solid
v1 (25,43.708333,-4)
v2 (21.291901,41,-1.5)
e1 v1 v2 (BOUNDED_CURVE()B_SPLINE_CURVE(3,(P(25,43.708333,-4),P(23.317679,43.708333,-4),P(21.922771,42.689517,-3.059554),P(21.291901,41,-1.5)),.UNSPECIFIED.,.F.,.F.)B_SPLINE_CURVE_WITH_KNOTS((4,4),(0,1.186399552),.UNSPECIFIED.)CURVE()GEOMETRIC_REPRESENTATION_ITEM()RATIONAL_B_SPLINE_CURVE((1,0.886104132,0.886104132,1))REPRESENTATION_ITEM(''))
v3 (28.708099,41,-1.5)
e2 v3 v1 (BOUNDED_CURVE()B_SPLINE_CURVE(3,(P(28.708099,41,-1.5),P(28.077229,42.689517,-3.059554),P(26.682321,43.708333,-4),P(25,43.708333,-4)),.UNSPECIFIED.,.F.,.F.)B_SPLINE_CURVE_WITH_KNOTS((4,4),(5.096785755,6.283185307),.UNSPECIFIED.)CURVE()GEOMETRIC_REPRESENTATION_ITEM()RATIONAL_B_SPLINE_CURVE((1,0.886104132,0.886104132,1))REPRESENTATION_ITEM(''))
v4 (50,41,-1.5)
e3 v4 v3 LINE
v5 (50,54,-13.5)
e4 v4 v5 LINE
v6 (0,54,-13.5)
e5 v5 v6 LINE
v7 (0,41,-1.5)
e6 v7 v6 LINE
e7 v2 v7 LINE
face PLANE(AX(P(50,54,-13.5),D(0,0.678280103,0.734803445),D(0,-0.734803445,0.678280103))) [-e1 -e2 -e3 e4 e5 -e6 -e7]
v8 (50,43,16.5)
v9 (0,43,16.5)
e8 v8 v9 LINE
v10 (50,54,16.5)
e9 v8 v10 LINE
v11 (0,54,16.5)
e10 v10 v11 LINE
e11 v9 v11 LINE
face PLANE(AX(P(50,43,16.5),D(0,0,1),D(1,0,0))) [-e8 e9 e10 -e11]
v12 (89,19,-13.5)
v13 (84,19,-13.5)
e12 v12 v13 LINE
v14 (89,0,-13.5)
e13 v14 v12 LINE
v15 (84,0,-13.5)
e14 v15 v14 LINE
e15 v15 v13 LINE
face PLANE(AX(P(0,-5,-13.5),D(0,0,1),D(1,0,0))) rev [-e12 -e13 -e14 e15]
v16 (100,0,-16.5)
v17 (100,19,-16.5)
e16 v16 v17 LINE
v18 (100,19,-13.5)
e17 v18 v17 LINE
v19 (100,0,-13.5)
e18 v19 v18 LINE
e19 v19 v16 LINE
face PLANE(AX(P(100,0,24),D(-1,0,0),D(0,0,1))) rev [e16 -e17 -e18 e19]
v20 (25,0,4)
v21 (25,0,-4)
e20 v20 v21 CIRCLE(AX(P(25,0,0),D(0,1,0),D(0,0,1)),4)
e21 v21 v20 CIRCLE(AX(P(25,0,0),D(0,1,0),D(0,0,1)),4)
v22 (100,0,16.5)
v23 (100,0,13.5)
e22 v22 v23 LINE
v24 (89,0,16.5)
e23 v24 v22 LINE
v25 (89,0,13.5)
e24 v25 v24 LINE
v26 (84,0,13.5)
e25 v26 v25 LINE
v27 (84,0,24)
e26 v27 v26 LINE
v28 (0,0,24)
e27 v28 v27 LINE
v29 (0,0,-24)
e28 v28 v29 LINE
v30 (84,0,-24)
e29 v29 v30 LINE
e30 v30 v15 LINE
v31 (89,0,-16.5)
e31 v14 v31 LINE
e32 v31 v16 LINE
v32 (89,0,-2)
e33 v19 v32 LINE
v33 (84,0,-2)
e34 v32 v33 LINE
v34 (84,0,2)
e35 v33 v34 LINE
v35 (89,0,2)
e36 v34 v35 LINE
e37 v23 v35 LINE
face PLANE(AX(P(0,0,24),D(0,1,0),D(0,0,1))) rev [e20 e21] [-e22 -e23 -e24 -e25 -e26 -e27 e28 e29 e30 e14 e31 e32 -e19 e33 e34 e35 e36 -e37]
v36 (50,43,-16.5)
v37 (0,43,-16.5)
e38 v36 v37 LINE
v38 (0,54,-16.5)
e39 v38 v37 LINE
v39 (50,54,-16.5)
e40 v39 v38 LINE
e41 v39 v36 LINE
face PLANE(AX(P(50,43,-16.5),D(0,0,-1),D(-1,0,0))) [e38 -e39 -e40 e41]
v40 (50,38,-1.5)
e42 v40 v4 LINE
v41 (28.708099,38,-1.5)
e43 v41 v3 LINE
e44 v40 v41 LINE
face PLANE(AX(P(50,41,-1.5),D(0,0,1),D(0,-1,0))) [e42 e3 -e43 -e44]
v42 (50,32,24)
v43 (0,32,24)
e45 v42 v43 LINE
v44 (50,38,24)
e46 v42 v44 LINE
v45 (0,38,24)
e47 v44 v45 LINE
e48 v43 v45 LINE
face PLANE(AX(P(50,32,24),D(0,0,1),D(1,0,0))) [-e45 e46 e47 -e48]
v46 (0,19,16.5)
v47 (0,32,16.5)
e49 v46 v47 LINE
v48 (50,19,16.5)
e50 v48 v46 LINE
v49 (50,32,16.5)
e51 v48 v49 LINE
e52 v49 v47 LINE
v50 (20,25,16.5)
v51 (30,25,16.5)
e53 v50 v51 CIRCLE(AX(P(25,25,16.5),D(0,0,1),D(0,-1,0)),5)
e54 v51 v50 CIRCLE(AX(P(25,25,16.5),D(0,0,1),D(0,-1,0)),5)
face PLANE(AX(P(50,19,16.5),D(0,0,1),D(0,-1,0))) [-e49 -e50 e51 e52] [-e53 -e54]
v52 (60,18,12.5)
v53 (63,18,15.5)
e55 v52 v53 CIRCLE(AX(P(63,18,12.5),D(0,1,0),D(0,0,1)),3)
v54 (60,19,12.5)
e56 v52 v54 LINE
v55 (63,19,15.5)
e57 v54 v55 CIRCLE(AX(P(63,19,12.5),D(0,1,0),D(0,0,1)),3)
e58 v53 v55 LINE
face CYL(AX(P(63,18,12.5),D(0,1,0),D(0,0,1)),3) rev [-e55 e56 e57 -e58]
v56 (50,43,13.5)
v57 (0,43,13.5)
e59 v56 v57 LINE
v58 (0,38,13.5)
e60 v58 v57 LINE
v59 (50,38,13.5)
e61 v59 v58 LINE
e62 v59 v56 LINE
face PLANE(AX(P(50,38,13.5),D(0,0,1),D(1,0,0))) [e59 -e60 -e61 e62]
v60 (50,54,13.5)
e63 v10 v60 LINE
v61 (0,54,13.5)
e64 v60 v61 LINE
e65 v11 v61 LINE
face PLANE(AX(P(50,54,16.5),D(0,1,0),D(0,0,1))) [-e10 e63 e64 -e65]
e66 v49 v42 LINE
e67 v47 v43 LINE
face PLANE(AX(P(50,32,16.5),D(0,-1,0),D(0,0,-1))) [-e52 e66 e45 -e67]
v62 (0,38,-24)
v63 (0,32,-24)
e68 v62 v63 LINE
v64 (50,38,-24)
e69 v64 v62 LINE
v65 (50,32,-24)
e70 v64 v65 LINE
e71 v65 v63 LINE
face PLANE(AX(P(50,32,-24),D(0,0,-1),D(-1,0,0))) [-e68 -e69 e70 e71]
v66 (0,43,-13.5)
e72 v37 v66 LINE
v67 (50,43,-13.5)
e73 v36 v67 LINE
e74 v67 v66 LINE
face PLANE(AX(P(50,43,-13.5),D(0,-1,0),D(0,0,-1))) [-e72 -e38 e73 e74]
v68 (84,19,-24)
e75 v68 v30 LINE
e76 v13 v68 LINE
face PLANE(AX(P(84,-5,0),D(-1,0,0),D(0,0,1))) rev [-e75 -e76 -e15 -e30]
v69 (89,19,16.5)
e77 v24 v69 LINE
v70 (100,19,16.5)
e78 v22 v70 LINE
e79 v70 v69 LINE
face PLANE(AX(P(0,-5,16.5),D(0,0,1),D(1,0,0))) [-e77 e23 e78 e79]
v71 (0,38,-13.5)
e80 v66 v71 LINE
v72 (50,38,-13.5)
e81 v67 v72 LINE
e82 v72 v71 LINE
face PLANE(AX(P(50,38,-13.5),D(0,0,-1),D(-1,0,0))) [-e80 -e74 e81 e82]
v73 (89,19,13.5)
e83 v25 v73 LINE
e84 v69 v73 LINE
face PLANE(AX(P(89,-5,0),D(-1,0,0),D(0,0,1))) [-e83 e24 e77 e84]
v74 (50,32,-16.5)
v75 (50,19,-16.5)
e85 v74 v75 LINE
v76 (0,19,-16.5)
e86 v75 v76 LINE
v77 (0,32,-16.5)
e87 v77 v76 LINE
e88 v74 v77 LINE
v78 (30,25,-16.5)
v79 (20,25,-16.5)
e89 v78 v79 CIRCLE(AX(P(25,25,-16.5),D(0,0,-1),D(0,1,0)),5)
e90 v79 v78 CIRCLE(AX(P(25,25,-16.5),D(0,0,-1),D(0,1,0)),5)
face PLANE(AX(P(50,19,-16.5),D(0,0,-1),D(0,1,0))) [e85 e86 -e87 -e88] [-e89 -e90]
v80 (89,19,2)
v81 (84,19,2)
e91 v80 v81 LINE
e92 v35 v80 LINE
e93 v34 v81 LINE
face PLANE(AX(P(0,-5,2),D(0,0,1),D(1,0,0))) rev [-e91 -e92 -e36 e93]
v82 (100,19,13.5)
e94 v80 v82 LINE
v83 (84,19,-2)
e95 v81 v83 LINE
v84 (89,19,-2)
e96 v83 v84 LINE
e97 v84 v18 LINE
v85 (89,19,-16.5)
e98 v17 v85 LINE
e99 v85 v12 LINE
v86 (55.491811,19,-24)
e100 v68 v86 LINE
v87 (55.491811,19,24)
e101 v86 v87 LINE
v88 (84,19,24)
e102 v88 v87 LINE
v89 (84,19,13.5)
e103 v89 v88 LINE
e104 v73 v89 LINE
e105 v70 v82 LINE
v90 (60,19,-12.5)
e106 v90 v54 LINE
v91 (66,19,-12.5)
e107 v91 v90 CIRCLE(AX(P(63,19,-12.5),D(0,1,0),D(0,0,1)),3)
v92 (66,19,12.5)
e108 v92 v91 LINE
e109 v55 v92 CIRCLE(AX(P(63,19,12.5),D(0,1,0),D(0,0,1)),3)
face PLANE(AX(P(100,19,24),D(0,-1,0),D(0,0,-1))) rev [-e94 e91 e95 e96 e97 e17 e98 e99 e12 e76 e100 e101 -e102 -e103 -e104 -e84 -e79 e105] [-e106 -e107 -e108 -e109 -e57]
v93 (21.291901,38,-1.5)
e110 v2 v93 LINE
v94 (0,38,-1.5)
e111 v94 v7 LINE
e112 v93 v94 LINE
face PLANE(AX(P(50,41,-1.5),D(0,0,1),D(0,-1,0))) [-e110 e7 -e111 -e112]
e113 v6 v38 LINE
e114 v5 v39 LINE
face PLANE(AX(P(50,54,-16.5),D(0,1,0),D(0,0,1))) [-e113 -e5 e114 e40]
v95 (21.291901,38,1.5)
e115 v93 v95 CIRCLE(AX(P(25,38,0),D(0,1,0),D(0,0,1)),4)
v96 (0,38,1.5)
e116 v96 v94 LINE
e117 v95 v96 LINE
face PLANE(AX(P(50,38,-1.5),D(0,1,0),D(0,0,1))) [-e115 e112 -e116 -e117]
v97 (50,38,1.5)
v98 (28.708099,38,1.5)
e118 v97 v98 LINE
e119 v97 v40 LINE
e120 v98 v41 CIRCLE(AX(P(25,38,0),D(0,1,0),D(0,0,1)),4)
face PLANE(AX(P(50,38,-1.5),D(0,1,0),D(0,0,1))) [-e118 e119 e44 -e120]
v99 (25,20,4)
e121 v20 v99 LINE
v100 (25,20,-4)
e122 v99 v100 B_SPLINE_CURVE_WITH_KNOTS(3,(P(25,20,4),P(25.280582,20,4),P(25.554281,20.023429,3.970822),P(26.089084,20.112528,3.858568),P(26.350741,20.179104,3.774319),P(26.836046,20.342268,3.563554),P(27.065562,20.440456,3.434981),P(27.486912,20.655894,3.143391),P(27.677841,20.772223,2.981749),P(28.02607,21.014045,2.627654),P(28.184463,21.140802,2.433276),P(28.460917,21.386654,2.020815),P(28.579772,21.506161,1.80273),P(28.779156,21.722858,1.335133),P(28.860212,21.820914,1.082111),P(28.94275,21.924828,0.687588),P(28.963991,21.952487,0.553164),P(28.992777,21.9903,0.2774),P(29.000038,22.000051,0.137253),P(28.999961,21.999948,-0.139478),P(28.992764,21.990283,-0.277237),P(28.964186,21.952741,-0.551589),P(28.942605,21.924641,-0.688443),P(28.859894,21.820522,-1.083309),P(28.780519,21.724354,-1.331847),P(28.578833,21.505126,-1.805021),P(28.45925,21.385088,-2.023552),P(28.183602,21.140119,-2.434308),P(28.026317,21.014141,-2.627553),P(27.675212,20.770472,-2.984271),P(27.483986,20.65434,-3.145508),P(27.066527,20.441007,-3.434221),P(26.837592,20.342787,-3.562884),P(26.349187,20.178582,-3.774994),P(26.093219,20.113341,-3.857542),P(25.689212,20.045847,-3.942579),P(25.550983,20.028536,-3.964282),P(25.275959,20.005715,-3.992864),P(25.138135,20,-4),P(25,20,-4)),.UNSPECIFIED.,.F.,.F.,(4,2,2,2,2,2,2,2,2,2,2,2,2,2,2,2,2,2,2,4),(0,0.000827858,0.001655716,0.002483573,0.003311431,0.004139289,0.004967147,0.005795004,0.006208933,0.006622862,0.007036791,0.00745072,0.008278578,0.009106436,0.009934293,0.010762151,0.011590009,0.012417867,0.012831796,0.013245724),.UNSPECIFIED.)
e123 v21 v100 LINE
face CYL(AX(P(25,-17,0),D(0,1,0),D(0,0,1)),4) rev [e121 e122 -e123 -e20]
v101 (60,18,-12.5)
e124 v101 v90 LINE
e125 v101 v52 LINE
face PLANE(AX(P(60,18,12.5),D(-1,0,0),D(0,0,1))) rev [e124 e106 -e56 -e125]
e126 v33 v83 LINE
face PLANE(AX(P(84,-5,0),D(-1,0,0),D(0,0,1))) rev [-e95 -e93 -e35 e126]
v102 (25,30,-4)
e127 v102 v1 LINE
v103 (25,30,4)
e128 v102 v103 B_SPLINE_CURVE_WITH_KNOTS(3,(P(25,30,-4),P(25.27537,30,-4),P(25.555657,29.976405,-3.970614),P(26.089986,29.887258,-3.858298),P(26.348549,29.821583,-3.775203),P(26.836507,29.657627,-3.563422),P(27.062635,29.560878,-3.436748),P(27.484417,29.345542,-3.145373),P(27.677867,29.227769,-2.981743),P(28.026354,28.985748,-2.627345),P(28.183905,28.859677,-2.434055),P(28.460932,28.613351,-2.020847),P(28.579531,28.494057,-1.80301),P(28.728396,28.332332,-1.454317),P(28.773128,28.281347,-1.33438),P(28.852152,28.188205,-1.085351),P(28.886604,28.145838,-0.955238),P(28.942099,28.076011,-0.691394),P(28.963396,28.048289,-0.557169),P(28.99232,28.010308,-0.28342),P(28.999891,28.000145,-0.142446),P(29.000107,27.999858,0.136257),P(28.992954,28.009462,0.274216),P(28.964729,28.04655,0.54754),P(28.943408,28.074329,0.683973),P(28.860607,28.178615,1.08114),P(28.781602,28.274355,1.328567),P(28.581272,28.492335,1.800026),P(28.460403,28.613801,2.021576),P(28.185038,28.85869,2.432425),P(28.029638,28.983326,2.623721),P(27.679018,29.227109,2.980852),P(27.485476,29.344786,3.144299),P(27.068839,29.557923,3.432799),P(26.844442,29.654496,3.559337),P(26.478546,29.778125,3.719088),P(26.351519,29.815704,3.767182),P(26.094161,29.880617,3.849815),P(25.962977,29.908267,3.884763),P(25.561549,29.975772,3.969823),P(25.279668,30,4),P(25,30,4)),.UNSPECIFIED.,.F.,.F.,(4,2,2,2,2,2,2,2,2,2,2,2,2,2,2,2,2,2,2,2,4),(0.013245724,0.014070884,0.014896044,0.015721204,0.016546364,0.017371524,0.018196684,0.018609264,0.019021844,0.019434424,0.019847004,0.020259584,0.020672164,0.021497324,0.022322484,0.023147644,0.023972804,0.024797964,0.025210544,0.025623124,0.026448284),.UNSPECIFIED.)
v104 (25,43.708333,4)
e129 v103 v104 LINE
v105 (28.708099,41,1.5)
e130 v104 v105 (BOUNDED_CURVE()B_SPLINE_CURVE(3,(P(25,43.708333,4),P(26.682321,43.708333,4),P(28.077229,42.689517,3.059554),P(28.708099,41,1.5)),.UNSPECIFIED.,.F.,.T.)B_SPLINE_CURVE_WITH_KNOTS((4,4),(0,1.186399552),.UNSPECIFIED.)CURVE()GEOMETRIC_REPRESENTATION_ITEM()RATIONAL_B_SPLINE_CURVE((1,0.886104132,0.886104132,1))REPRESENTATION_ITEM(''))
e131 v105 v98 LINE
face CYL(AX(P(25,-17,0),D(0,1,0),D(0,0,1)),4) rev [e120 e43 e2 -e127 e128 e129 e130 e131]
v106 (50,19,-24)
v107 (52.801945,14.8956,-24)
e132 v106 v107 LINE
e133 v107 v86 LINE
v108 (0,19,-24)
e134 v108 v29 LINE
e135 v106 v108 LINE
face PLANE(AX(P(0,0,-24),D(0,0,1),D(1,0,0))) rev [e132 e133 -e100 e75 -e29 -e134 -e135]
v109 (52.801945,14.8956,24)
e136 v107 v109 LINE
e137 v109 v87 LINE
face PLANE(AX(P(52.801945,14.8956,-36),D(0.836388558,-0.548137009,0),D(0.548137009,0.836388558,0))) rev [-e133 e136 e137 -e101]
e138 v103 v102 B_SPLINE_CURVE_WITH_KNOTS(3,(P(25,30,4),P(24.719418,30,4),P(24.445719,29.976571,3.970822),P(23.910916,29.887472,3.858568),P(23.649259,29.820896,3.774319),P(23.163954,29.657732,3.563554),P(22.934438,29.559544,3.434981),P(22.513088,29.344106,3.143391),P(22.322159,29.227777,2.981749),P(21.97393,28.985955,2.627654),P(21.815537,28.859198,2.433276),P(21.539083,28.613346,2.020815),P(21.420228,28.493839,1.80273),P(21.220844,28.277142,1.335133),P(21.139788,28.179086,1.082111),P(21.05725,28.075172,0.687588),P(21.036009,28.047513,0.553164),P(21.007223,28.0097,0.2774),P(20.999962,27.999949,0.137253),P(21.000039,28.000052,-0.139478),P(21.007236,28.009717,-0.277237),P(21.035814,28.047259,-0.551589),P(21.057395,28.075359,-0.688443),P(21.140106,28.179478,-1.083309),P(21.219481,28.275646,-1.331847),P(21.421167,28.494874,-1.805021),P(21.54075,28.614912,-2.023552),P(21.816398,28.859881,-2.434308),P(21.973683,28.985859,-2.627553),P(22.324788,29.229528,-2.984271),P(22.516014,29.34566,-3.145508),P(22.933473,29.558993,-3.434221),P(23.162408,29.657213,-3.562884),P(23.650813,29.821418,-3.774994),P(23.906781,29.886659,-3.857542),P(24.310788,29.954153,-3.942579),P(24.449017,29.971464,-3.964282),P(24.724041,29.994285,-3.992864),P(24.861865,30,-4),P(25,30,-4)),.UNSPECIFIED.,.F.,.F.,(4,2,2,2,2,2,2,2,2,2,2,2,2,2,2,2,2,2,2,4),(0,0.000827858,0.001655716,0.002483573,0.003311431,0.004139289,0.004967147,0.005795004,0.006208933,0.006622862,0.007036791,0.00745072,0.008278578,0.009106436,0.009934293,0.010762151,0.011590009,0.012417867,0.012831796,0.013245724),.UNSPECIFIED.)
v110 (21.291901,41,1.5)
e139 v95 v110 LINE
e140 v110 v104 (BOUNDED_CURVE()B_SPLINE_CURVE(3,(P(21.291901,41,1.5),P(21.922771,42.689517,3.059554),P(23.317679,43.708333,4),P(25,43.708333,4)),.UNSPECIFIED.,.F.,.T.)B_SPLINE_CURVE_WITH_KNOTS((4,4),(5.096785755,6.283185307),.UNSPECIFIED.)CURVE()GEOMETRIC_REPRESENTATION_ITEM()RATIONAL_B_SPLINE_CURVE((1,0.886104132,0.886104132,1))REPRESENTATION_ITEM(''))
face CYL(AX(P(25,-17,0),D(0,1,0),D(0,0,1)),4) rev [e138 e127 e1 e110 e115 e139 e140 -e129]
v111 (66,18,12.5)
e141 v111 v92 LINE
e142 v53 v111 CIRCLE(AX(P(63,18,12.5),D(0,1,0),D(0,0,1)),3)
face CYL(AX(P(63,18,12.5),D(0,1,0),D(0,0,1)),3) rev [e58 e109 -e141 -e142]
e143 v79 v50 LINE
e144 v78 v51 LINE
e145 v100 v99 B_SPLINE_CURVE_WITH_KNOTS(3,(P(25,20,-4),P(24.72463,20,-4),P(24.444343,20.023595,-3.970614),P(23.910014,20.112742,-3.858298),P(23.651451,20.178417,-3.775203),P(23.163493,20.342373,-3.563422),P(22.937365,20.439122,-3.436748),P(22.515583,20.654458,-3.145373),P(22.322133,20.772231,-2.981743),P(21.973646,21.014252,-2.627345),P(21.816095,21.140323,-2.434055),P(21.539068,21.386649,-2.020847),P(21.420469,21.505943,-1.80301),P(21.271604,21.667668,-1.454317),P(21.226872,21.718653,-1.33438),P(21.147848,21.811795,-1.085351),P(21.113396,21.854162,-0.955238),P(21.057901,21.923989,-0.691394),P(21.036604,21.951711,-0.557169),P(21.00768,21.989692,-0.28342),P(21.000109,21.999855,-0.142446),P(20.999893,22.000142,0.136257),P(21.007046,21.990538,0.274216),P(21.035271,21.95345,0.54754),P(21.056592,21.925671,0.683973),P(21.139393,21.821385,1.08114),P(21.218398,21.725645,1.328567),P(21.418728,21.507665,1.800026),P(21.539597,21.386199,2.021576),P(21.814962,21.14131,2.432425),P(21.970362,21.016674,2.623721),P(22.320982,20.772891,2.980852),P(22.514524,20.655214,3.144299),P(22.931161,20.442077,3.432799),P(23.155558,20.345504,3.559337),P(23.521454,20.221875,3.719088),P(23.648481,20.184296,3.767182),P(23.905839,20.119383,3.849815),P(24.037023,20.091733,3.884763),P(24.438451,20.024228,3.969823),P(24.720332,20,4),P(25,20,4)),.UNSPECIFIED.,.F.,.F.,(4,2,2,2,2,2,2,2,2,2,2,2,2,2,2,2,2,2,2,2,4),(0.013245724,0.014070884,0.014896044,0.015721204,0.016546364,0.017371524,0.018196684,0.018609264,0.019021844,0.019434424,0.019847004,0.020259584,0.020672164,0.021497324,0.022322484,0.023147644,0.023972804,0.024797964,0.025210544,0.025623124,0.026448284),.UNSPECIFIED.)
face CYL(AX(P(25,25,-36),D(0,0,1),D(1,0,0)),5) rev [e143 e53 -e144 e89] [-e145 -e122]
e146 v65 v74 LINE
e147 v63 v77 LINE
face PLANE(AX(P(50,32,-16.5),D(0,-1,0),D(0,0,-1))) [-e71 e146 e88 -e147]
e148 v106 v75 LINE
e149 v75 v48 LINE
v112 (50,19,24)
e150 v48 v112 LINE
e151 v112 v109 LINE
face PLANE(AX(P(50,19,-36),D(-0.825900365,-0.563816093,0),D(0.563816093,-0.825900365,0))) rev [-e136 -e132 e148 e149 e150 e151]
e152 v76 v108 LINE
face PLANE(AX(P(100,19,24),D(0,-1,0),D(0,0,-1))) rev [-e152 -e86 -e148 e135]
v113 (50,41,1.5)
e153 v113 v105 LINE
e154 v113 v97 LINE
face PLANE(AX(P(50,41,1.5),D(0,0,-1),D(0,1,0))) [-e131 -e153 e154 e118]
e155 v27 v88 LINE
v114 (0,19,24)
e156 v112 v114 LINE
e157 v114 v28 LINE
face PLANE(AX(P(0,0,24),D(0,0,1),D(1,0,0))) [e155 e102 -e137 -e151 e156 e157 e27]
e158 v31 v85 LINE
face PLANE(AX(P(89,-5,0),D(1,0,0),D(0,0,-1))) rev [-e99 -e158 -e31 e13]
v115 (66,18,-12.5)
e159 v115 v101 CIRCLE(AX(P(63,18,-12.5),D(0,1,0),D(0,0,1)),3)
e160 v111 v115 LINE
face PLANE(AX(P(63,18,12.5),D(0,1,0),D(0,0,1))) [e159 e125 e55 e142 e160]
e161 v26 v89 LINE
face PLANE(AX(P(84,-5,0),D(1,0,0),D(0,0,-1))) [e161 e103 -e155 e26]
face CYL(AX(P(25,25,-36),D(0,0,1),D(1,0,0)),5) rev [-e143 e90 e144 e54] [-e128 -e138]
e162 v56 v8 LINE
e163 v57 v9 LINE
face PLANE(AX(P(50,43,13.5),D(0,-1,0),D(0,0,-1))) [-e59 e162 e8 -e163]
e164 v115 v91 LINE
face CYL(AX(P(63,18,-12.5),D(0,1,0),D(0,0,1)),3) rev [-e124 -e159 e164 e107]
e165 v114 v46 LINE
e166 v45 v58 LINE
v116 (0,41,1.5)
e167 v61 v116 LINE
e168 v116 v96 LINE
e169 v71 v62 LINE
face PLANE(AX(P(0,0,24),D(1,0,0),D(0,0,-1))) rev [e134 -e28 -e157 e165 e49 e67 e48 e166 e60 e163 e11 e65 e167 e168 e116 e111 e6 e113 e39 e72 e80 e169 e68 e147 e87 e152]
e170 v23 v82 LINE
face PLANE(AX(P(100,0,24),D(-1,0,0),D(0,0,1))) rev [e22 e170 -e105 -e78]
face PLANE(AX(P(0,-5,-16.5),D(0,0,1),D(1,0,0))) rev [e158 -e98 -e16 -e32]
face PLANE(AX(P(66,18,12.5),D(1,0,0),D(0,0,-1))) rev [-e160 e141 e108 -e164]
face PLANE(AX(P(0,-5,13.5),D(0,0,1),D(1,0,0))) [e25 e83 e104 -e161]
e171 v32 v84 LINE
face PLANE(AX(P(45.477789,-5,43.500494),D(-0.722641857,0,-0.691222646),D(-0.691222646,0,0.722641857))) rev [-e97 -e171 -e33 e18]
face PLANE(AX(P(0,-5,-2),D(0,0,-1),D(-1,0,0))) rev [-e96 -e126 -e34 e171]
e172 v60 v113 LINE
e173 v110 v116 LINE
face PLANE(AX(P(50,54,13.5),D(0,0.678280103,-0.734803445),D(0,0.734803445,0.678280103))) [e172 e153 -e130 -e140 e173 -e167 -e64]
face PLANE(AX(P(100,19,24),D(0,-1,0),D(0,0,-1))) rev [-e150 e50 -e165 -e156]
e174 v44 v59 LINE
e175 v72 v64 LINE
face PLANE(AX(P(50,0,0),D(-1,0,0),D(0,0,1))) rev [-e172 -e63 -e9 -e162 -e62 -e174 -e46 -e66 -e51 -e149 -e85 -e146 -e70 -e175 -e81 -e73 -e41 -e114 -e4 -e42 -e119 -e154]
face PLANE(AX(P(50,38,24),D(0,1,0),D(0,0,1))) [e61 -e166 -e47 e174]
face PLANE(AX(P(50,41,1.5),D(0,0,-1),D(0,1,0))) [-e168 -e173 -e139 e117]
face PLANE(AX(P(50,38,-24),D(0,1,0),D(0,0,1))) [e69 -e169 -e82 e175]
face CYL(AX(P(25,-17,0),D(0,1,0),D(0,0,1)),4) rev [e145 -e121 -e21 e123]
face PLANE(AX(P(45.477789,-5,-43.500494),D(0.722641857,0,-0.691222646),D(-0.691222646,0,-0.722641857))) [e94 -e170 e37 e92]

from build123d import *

# Parameters (mm, degrees)
BASE_BLOCK_PROFILE_W          = 100
BASE_BLOCK_PROFILE_H          = 19
BASE_BLOCK_100X19X48_DEPTH    = 24
END_NOTCHES_CUT_DEPTH         = 24
GUIDE_SLOT_63X3_DEPTH_1_DEPTH = 1
V_BLOCK_BODY_DEPTH            = 50
V_GROOVE_CUT_DEPTH            = 60
CROSS_HOLE_8_SKETCH_R         = 4
CROSS_HOLE_8_DEPTH            = 55
HOLE_10_SKETCH_R              = 5
HOLE_10_DEPTH                 = 60


with BuildPart() as part:
    # Base Block Profile → Base Block 100x19x48 (new, symmetric)
    with BuildSketch(Plane.XY):
        with Locations((50, 9.5)):
            Rectangle(BASE_BLOCK_PROFILE_W, BASE_BLOCK_PROFILE_H)
    extrude(amount=BASE_BLOCK_100X19X48_DEPTH, both=True)

    # End Notch Profile → End Notches Cut (cut, symmetric)
    with BuildSketch(Plane(origin=(0, 19, 0), x_dir=(1, 0, 0), z_dir=(0, 1, 0))):
        Polygon((100, -24), (100, -16.5), (89, -16.5), (89, -13.5), (84, -13.5), (84, -24), align=None)
        Polygon((100, -13.5), (100, 0), (84, 0), (84, -2), (89, -2), align=None)
        Polygon((100, 0), (100, 13.5), (89, 2), (84, 2), (84, 0), align=None)
        Polygon((100, 24), (84, 24), (84, 13.5), (89, 13.5), (89, 16.5), (100, 16.5), align=None)
    extrude(amount=END_NOTCHES_CUT_DEPTH, both=True, mode=Mode.SUBTRACT)

    # Guide Slot Sketch → Guide Slot 63x3 Depth 1 (cut)
    with BuildSketch(Plane(origin=(0, 19, 0), x_dir=(1, 0, 0), z_dir=(0, 1, 0))):
        with BuildLine():
            Line((60, -12.5), (60, 12.5))
            ThreePointArc((60, 12.5), (63, 15.5), (66, 12.5))
            Line((66, 12.5), (66, -12.5))
            ThreePointArc((66, -12.5), (63, -15.5), (60, -12.5))
        make_face()
    extrude(amount=-GUIDE_SLOT_63X3_DEPTH_1_DEPTH, mode=Mode.SUBTRACT)

    # V-Block Body Profile → V-Block Body (add)
    with BuildSketch(Plane.ZY):
        Polygon((-16.5, 19), (-16.5, 32), (-24, 32), (-24, 38), (-13.5, 38), (-13.5, 43), (-16.5, 43), (-16.5, 54), (-13.5, 54), (-1.5, 41), (-1.5, 38), (1.5, 38), (1.5, 41), (13.5, 54), (16.5, 54), (16.5, 43), (13.5, 43), (13.5, 38), (24, 38), (24, 32), (16.5, 32), (16.5, 19), align=None)
    extrude(amount=-V_BLOCK_BODY_DEPTH)

    # V-Groove Sketch → V-Groove Cut (cut)
    with BuildSketch(Plane.XY.offset(24)):
        Polygon((50, 19), (52.80194455, 14.895599546), (55.491811317, 19), align=None)
    extrude(amount=-V_GROOVE_CUT_DEPTH, mode=Mode.SUBTRACT)

    # Cross Hole Ø8 Sketch → Cross Hole Ø8 (cut, symmetric)
    with BuildSketch(Plane(origin=(0, 38, 0), x_dir=(1, 0, 0), z_dir=(0, 1, 0))):
        with Locations(Location((25, 0, 0), (0, 0, 270))):
            Circle(CROSS_HOLE_8_SKETCH_R)
    extrude(amount=CROSS_HOLE_8_DEPTH, both=True, mode=Mode.SUBTRACT)

    # Hole Ø10 Sketch → Hole Ø10 (cut)
    with BuildSketch(Plane.XY.offset(24)):
        with Locations(Location((25, 25, 0), (0, 0, 90))):
            Circle(HOLE_10_SKETCH_R)
    extrude(amount=-HOLE_10_DEPTH, mode=Mode.SUBTRACT)


solid = part.part
